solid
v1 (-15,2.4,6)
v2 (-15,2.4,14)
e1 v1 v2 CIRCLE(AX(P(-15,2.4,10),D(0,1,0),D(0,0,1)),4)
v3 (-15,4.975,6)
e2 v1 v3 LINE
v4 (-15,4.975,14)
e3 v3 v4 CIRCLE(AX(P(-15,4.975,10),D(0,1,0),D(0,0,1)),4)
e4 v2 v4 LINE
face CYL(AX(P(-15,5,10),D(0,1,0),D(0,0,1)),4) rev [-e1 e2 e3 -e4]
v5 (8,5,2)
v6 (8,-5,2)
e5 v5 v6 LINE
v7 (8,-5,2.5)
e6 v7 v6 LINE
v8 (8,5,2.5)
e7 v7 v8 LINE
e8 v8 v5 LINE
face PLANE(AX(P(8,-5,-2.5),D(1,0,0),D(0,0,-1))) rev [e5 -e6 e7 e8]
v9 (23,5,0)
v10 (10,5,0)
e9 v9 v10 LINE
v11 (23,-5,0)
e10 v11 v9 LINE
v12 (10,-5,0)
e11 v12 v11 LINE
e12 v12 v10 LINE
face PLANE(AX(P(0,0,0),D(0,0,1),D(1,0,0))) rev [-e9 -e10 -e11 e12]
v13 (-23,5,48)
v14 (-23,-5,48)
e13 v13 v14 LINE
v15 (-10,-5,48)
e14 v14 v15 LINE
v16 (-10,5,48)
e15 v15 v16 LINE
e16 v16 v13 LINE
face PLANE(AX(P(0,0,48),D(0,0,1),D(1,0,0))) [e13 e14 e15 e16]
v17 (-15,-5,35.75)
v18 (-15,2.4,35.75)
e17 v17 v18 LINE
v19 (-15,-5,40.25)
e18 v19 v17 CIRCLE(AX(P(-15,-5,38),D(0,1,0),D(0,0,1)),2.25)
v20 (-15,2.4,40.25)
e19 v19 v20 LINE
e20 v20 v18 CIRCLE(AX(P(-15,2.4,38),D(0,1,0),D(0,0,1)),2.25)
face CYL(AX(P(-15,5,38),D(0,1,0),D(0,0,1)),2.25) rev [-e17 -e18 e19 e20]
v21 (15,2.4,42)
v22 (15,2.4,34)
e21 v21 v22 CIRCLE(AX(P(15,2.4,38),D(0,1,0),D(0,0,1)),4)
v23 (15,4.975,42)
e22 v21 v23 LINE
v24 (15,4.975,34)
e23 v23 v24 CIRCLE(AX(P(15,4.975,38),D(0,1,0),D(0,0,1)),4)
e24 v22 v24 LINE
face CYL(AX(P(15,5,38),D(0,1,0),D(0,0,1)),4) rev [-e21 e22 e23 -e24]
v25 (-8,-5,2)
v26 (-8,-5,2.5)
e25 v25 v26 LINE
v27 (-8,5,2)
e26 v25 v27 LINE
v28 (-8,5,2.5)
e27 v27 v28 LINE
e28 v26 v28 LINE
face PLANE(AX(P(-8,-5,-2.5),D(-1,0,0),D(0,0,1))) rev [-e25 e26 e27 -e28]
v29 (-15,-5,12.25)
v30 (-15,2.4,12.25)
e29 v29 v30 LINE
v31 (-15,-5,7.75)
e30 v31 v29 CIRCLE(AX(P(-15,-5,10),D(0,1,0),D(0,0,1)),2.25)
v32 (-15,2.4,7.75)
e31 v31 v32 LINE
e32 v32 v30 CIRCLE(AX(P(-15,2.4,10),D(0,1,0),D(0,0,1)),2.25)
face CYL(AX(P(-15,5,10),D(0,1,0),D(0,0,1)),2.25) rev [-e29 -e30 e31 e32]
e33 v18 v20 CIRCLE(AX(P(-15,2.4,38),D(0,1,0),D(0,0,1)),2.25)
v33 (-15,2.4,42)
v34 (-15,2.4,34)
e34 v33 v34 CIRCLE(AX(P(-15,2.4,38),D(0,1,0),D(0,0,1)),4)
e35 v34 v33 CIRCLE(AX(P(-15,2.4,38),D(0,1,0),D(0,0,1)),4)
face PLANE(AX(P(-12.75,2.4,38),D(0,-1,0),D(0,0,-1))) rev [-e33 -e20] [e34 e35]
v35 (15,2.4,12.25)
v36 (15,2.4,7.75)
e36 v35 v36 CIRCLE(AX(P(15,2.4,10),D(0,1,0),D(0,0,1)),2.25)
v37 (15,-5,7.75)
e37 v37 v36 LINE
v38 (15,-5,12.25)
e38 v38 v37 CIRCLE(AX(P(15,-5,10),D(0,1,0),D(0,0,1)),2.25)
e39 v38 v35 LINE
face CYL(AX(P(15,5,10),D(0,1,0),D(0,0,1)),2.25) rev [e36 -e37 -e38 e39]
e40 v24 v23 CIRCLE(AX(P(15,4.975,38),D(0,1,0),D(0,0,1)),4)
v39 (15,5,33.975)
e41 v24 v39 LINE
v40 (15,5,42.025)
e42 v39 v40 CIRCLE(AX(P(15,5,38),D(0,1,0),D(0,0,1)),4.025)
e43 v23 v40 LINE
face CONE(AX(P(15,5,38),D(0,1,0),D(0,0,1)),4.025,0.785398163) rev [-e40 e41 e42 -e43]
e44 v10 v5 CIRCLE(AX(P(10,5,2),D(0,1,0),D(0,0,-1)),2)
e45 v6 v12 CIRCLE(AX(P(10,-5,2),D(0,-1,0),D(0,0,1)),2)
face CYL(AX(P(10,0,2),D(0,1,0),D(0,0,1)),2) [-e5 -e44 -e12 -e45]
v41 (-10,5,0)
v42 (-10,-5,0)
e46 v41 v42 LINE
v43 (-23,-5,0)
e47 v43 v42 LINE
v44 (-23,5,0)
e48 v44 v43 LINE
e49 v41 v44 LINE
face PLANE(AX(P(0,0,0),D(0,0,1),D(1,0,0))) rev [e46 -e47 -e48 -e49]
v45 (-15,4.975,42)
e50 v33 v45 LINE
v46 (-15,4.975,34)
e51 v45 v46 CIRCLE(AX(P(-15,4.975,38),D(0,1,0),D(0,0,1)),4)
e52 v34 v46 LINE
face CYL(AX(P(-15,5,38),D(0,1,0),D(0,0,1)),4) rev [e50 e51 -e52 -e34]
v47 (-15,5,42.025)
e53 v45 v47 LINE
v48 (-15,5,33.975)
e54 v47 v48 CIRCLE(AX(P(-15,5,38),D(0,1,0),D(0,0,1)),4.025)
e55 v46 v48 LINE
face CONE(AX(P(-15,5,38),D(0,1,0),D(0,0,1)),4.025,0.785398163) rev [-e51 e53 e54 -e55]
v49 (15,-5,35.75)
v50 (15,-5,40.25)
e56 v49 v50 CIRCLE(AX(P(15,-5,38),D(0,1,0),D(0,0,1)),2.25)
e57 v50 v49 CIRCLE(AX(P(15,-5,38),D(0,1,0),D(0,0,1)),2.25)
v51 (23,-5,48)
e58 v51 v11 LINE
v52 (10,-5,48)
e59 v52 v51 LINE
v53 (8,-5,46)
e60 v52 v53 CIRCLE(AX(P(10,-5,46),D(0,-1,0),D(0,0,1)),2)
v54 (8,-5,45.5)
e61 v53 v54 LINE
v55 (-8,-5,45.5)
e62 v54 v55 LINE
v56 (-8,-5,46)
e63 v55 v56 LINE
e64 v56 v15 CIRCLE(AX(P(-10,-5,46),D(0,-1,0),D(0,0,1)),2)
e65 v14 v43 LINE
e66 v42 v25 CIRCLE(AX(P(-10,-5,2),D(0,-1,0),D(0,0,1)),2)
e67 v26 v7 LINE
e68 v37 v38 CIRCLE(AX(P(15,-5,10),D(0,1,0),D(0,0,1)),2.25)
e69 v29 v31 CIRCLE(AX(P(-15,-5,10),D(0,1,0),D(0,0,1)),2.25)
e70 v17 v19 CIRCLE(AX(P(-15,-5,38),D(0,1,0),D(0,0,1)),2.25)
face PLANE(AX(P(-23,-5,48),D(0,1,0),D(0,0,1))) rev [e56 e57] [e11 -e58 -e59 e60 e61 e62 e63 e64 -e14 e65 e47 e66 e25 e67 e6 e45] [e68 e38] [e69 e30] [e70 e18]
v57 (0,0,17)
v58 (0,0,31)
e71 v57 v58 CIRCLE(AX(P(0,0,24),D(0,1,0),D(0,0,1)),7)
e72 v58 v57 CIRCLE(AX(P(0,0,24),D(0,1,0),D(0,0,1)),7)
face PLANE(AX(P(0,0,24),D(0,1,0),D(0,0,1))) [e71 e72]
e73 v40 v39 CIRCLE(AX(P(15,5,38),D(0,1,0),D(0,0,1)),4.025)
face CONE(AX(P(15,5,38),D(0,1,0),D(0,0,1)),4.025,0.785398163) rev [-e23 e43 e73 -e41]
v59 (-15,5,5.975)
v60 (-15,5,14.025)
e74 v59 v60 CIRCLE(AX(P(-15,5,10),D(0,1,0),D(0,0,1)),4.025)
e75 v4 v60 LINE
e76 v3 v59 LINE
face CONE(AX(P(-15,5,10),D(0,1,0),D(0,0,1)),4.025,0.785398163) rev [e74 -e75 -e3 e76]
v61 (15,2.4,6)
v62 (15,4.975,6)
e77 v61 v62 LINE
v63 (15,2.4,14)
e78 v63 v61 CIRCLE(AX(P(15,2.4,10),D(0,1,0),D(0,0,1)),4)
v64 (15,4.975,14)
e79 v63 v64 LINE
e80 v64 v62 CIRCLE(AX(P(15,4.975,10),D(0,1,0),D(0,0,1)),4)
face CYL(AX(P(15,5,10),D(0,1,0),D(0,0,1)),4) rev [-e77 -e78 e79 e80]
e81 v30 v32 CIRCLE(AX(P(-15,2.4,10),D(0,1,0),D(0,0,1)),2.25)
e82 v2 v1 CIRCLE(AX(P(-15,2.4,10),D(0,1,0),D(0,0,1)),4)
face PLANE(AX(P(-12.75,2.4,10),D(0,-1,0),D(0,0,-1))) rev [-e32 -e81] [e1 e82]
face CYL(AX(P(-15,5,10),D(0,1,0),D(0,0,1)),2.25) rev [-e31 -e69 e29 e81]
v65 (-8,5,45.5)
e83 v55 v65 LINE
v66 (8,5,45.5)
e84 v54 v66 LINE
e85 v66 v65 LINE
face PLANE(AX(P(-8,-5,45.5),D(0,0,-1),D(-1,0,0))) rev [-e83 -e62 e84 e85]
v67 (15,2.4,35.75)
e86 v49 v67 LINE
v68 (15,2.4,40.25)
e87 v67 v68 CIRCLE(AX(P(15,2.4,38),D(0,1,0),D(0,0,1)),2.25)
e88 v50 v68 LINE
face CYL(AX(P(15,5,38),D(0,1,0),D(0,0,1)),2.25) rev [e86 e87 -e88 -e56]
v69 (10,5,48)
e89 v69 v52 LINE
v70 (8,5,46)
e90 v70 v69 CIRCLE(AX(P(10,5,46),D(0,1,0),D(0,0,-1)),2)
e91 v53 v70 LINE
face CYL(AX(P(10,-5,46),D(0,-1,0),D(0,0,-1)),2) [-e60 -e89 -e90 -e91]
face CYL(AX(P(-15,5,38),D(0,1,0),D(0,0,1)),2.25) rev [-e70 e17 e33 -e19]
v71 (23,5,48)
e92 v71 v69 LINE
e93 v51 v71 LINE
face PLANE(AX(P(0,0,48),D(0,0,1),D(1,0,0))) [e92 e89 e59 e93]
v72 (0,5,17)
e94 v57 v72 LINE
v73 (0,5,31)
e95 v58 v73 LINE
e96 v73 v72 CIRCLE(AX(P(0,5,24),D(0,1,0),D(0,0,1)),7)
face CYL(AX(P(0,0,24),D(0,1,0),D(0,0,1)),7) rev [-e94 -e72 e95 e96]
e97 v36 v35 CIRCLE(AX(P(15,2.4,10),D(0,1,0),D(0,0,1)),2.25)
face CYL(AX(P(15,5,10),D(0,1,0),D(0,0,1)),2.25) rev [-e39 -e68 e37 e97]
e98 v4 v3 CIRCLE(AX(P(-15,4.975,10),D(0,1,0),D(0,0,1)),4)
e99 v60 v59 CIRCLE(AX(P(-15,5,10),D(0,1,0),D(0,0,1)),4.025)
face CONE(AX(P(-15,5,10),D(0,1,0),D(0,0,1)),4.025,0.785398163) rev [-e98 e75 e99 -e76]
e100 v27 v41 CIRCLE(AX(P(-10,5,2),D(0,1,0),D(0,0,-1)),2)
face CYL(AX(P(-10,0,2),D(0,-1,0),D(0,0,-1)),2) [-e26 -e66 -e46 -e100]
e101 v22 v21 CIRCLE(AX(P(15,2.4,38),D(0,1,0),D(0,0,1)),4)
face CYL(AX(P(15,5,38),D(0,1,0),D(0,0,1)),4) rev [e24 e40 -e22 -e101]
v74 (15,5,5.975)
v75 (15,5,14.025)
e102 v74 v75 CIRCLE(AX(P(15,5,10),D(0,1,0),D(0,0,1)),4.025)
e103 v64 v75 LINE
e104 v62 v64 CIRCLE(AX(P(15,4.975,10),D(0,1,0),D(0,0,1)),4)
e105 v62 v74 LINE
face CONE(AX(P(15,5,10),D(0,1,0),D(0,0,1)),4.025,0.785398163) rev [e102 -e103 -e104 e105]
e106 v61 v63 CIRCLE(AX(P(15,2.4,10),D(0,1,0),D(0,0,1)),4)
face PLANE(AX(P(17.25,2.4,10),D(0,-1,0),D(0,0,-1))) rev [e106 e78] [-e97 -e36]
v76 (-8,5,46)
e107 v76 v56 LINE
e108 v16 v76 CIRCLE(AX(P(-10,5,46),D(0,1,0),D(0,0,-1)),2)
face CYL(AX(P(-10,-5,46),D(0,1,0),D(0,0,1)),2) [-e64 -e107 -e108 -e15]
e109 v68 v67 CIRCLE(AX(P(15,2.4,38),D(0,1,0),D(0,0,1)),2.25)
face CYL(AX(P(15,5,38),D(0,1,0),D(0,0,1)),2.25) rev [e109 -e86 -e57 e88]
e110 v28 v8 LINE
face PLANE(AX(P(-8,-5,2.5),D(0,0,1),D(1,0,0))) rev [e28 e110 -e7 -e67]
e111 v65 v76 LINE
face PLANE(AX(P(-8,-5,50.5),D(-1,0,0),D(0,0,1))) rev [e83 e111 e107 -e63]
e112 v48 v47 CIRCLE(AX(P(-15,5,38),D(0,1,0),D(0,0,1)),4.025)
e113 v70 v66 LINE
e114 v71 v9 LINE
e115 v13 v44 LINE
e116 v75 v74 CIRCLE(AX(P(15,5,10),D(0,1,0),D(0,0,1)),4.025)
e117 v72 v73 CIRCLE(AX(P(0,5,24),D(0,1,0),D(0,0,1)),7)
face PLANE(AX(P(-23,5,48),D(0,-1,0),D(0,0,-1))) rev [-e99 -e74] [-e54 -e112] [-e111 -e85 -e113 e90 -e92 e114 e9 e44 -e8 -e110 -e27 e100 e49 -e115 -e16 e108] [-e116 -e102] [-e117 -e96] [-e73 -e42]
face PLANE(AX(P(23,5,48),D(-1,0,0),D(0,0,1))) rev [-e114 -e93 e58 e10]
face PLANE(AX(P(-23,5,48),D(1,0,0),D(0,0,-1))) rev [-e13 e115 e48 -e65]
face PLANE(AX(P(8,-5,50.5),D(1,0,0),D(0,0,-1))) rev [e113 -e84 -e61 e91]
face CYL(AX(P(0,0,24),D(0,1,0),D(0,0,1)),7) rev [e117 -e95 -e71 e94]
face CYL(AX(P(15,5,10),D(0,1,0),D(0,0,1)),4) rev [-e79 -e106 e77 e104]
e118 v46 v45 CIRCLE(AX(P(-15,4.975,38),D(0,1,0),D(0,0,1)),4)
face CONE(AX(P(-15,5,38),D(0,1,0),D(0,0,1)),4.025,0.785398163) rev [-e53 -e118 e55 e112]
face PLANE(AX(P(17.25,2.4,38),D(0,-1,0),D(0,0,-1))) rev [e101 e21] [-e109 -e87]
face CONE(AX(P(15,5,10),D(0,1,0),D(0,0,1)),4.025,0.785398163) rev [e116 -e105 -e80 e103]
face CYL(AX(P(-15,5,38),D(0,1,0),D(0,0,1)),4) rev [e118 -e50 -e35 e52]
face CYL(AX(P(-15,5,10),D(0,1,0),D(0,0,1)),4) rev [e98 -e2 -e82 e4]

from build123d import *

# Parameters (mm, degrees)
SKETCH1_W                                  = 46
SKETCH1_H                                  = 10
BOSS_EXTRUDE1_DEPTH                        = 48
SKETCH2_W                                  = 16
SKETCH2_H                                  = 5
CUT_EXTRUDE1_DEPTH                         = 10
FILLET1_R                                  = 2
CBORE_FOR_M4_CHEESE_HEAD_SCREW1_AT_2_COUNT = 2
CBORE_FOR_M4_CHEESE_HEAD_SCREW1_AT_2_PITCH = 28
CBORE_FOR_M4_CHEESE_HEAD_SCREW1_AT_3_COUNT = 2
CBORE_FOR_M4_CHEESE_HEAD_SCREW1_AT_3_PITCH = 41.036569057
CBORE_FOR_M4_CHEESE_HEAD_SCREW1_AT_4_COUNT = 2
CBORE_FOR_M4_CHEESE_HEAD_SCREW1_AT_4_PITCH = 30
SKETCH6_R                                  = 7
CUT_EXTRUDE2_DEPTH                         = 5


with BuildPart() as part:
    # Sketch1 → Boss-Extrude1 (new body)
    with BuildSketch(Plane.XY):
        Rectangle(SKETCH1_W, SKETCH1_H)
    extrude(amount=BOSS_EXTRUDE1_DEPTH)

    # Sketch2 → Cut-Extrude1 (cut)
    with BuildSketch(Plane(origin=(0, 5, 0), x_dir=(1, 0, 0), z_dir=(0, 1, 0))):
        with Locations((0, -48)):
            Rectangle(SKETCH2_W, SKETCH2_H)
        Rectangle(SKETCH2_W, SKETCH2_H)
    extrude(amount=-CUT_EXTRUDE1_DEPTH, mode=Mode.SUBTRACT)

    # Fillet1
    fillet1_edges = [part.edges().sort_by_distance(p)[0] for p in [
        (-8, 0, 0),
        (8, 0, 0),
        (8, 0, 48),
        (-8, 0, 48),
    ]]
    fillet(fillet1_edges, radius=FILLET1_R)

    # Sketch4 → CBORE for M4 Cheese Head Screw1 (revolve, cut)
    with BuildSketch(Plane(origin=(-15, 5, 10), x_dir=(0, 0, 1), z_dir=(1, 0, 0))):
        Polygon((0, 0), (0, 11.351936393), (2.25, 10), (2.25, 2.6), (4, 2.6), (4, 0.025), (4.025, 0), align=None)
    cbore_for_m4_cheese_head_screw1 = revolve(axis=Axis((-15, 11.35, 10), (0, -1, 0)), mode=Mode.SUBTRACT)

    # CBORE for M4 Cheese Head Screw1 at 2: CBORE for M4 Cheese Head Screw1 ×2
    with Locations(*[(0, 0, i * CBORE_FOR_M4_CHEESE_HEAD_SCREW1_AT_2_PITCH) for i in range(1, CBORE_FOR_M4_CHEESE_HEAD_SCREW1_AT_2_COUNT)]):
        add(cbore_for_m4_cheese_head_screw1, mode=Mode.SUBTRACT)

    # CBORE for M4 Cheese Head Screw1 at 3: CBORE for M4 Cheese Head Screw1 ×2
    with Locations(*[Vector(0.731055268242869, 0, 0.6823182503600111) * (i * CBORE_FOR_M4_CHEESE_HEAD_SCREW1_AT_3_PITCH) for i in range(1, CBORE_FOR_M4_CHEESE_HEAD_SCREW1_AT_3_COUNT)]):
        add(cbore_for_m4_cheese_head_screw1, mode=Mode.SUBTRACT)

    # CBORE for M4 Cheese Head Screw1 at 4: CBORE for M4 Cheese Head Screw1 ×2
    with Locations(*[(i * CBORE_FOR_M4_CHEESE_HEAD_SCREW1_AT_4_PITCH, 0, 0) for i in range(1, CBORE_FOR_M4_CHEESE_HEAD_SCREW1_AT_4_COUNT)]):
        add(cbore_for_m4_cheese_head_screw1, mode=Mode.SUBTRACT)

    # Sketch6 → Cut-Extrude2 (cut)
    with BuildSketch(Plane(origin=(0, 5, 0), x_dir=(1, 0, 0), z_dir=(0, 1, 0))):
        with Locations(Location((0, -24, 0), (0, 0, 270))):
            Circle(SKETCH6_R)
    extrude(amount=-CUT_EXTRUDE2_DEPTH, mode=Mode.SUBTRACT)


solid = part.part
